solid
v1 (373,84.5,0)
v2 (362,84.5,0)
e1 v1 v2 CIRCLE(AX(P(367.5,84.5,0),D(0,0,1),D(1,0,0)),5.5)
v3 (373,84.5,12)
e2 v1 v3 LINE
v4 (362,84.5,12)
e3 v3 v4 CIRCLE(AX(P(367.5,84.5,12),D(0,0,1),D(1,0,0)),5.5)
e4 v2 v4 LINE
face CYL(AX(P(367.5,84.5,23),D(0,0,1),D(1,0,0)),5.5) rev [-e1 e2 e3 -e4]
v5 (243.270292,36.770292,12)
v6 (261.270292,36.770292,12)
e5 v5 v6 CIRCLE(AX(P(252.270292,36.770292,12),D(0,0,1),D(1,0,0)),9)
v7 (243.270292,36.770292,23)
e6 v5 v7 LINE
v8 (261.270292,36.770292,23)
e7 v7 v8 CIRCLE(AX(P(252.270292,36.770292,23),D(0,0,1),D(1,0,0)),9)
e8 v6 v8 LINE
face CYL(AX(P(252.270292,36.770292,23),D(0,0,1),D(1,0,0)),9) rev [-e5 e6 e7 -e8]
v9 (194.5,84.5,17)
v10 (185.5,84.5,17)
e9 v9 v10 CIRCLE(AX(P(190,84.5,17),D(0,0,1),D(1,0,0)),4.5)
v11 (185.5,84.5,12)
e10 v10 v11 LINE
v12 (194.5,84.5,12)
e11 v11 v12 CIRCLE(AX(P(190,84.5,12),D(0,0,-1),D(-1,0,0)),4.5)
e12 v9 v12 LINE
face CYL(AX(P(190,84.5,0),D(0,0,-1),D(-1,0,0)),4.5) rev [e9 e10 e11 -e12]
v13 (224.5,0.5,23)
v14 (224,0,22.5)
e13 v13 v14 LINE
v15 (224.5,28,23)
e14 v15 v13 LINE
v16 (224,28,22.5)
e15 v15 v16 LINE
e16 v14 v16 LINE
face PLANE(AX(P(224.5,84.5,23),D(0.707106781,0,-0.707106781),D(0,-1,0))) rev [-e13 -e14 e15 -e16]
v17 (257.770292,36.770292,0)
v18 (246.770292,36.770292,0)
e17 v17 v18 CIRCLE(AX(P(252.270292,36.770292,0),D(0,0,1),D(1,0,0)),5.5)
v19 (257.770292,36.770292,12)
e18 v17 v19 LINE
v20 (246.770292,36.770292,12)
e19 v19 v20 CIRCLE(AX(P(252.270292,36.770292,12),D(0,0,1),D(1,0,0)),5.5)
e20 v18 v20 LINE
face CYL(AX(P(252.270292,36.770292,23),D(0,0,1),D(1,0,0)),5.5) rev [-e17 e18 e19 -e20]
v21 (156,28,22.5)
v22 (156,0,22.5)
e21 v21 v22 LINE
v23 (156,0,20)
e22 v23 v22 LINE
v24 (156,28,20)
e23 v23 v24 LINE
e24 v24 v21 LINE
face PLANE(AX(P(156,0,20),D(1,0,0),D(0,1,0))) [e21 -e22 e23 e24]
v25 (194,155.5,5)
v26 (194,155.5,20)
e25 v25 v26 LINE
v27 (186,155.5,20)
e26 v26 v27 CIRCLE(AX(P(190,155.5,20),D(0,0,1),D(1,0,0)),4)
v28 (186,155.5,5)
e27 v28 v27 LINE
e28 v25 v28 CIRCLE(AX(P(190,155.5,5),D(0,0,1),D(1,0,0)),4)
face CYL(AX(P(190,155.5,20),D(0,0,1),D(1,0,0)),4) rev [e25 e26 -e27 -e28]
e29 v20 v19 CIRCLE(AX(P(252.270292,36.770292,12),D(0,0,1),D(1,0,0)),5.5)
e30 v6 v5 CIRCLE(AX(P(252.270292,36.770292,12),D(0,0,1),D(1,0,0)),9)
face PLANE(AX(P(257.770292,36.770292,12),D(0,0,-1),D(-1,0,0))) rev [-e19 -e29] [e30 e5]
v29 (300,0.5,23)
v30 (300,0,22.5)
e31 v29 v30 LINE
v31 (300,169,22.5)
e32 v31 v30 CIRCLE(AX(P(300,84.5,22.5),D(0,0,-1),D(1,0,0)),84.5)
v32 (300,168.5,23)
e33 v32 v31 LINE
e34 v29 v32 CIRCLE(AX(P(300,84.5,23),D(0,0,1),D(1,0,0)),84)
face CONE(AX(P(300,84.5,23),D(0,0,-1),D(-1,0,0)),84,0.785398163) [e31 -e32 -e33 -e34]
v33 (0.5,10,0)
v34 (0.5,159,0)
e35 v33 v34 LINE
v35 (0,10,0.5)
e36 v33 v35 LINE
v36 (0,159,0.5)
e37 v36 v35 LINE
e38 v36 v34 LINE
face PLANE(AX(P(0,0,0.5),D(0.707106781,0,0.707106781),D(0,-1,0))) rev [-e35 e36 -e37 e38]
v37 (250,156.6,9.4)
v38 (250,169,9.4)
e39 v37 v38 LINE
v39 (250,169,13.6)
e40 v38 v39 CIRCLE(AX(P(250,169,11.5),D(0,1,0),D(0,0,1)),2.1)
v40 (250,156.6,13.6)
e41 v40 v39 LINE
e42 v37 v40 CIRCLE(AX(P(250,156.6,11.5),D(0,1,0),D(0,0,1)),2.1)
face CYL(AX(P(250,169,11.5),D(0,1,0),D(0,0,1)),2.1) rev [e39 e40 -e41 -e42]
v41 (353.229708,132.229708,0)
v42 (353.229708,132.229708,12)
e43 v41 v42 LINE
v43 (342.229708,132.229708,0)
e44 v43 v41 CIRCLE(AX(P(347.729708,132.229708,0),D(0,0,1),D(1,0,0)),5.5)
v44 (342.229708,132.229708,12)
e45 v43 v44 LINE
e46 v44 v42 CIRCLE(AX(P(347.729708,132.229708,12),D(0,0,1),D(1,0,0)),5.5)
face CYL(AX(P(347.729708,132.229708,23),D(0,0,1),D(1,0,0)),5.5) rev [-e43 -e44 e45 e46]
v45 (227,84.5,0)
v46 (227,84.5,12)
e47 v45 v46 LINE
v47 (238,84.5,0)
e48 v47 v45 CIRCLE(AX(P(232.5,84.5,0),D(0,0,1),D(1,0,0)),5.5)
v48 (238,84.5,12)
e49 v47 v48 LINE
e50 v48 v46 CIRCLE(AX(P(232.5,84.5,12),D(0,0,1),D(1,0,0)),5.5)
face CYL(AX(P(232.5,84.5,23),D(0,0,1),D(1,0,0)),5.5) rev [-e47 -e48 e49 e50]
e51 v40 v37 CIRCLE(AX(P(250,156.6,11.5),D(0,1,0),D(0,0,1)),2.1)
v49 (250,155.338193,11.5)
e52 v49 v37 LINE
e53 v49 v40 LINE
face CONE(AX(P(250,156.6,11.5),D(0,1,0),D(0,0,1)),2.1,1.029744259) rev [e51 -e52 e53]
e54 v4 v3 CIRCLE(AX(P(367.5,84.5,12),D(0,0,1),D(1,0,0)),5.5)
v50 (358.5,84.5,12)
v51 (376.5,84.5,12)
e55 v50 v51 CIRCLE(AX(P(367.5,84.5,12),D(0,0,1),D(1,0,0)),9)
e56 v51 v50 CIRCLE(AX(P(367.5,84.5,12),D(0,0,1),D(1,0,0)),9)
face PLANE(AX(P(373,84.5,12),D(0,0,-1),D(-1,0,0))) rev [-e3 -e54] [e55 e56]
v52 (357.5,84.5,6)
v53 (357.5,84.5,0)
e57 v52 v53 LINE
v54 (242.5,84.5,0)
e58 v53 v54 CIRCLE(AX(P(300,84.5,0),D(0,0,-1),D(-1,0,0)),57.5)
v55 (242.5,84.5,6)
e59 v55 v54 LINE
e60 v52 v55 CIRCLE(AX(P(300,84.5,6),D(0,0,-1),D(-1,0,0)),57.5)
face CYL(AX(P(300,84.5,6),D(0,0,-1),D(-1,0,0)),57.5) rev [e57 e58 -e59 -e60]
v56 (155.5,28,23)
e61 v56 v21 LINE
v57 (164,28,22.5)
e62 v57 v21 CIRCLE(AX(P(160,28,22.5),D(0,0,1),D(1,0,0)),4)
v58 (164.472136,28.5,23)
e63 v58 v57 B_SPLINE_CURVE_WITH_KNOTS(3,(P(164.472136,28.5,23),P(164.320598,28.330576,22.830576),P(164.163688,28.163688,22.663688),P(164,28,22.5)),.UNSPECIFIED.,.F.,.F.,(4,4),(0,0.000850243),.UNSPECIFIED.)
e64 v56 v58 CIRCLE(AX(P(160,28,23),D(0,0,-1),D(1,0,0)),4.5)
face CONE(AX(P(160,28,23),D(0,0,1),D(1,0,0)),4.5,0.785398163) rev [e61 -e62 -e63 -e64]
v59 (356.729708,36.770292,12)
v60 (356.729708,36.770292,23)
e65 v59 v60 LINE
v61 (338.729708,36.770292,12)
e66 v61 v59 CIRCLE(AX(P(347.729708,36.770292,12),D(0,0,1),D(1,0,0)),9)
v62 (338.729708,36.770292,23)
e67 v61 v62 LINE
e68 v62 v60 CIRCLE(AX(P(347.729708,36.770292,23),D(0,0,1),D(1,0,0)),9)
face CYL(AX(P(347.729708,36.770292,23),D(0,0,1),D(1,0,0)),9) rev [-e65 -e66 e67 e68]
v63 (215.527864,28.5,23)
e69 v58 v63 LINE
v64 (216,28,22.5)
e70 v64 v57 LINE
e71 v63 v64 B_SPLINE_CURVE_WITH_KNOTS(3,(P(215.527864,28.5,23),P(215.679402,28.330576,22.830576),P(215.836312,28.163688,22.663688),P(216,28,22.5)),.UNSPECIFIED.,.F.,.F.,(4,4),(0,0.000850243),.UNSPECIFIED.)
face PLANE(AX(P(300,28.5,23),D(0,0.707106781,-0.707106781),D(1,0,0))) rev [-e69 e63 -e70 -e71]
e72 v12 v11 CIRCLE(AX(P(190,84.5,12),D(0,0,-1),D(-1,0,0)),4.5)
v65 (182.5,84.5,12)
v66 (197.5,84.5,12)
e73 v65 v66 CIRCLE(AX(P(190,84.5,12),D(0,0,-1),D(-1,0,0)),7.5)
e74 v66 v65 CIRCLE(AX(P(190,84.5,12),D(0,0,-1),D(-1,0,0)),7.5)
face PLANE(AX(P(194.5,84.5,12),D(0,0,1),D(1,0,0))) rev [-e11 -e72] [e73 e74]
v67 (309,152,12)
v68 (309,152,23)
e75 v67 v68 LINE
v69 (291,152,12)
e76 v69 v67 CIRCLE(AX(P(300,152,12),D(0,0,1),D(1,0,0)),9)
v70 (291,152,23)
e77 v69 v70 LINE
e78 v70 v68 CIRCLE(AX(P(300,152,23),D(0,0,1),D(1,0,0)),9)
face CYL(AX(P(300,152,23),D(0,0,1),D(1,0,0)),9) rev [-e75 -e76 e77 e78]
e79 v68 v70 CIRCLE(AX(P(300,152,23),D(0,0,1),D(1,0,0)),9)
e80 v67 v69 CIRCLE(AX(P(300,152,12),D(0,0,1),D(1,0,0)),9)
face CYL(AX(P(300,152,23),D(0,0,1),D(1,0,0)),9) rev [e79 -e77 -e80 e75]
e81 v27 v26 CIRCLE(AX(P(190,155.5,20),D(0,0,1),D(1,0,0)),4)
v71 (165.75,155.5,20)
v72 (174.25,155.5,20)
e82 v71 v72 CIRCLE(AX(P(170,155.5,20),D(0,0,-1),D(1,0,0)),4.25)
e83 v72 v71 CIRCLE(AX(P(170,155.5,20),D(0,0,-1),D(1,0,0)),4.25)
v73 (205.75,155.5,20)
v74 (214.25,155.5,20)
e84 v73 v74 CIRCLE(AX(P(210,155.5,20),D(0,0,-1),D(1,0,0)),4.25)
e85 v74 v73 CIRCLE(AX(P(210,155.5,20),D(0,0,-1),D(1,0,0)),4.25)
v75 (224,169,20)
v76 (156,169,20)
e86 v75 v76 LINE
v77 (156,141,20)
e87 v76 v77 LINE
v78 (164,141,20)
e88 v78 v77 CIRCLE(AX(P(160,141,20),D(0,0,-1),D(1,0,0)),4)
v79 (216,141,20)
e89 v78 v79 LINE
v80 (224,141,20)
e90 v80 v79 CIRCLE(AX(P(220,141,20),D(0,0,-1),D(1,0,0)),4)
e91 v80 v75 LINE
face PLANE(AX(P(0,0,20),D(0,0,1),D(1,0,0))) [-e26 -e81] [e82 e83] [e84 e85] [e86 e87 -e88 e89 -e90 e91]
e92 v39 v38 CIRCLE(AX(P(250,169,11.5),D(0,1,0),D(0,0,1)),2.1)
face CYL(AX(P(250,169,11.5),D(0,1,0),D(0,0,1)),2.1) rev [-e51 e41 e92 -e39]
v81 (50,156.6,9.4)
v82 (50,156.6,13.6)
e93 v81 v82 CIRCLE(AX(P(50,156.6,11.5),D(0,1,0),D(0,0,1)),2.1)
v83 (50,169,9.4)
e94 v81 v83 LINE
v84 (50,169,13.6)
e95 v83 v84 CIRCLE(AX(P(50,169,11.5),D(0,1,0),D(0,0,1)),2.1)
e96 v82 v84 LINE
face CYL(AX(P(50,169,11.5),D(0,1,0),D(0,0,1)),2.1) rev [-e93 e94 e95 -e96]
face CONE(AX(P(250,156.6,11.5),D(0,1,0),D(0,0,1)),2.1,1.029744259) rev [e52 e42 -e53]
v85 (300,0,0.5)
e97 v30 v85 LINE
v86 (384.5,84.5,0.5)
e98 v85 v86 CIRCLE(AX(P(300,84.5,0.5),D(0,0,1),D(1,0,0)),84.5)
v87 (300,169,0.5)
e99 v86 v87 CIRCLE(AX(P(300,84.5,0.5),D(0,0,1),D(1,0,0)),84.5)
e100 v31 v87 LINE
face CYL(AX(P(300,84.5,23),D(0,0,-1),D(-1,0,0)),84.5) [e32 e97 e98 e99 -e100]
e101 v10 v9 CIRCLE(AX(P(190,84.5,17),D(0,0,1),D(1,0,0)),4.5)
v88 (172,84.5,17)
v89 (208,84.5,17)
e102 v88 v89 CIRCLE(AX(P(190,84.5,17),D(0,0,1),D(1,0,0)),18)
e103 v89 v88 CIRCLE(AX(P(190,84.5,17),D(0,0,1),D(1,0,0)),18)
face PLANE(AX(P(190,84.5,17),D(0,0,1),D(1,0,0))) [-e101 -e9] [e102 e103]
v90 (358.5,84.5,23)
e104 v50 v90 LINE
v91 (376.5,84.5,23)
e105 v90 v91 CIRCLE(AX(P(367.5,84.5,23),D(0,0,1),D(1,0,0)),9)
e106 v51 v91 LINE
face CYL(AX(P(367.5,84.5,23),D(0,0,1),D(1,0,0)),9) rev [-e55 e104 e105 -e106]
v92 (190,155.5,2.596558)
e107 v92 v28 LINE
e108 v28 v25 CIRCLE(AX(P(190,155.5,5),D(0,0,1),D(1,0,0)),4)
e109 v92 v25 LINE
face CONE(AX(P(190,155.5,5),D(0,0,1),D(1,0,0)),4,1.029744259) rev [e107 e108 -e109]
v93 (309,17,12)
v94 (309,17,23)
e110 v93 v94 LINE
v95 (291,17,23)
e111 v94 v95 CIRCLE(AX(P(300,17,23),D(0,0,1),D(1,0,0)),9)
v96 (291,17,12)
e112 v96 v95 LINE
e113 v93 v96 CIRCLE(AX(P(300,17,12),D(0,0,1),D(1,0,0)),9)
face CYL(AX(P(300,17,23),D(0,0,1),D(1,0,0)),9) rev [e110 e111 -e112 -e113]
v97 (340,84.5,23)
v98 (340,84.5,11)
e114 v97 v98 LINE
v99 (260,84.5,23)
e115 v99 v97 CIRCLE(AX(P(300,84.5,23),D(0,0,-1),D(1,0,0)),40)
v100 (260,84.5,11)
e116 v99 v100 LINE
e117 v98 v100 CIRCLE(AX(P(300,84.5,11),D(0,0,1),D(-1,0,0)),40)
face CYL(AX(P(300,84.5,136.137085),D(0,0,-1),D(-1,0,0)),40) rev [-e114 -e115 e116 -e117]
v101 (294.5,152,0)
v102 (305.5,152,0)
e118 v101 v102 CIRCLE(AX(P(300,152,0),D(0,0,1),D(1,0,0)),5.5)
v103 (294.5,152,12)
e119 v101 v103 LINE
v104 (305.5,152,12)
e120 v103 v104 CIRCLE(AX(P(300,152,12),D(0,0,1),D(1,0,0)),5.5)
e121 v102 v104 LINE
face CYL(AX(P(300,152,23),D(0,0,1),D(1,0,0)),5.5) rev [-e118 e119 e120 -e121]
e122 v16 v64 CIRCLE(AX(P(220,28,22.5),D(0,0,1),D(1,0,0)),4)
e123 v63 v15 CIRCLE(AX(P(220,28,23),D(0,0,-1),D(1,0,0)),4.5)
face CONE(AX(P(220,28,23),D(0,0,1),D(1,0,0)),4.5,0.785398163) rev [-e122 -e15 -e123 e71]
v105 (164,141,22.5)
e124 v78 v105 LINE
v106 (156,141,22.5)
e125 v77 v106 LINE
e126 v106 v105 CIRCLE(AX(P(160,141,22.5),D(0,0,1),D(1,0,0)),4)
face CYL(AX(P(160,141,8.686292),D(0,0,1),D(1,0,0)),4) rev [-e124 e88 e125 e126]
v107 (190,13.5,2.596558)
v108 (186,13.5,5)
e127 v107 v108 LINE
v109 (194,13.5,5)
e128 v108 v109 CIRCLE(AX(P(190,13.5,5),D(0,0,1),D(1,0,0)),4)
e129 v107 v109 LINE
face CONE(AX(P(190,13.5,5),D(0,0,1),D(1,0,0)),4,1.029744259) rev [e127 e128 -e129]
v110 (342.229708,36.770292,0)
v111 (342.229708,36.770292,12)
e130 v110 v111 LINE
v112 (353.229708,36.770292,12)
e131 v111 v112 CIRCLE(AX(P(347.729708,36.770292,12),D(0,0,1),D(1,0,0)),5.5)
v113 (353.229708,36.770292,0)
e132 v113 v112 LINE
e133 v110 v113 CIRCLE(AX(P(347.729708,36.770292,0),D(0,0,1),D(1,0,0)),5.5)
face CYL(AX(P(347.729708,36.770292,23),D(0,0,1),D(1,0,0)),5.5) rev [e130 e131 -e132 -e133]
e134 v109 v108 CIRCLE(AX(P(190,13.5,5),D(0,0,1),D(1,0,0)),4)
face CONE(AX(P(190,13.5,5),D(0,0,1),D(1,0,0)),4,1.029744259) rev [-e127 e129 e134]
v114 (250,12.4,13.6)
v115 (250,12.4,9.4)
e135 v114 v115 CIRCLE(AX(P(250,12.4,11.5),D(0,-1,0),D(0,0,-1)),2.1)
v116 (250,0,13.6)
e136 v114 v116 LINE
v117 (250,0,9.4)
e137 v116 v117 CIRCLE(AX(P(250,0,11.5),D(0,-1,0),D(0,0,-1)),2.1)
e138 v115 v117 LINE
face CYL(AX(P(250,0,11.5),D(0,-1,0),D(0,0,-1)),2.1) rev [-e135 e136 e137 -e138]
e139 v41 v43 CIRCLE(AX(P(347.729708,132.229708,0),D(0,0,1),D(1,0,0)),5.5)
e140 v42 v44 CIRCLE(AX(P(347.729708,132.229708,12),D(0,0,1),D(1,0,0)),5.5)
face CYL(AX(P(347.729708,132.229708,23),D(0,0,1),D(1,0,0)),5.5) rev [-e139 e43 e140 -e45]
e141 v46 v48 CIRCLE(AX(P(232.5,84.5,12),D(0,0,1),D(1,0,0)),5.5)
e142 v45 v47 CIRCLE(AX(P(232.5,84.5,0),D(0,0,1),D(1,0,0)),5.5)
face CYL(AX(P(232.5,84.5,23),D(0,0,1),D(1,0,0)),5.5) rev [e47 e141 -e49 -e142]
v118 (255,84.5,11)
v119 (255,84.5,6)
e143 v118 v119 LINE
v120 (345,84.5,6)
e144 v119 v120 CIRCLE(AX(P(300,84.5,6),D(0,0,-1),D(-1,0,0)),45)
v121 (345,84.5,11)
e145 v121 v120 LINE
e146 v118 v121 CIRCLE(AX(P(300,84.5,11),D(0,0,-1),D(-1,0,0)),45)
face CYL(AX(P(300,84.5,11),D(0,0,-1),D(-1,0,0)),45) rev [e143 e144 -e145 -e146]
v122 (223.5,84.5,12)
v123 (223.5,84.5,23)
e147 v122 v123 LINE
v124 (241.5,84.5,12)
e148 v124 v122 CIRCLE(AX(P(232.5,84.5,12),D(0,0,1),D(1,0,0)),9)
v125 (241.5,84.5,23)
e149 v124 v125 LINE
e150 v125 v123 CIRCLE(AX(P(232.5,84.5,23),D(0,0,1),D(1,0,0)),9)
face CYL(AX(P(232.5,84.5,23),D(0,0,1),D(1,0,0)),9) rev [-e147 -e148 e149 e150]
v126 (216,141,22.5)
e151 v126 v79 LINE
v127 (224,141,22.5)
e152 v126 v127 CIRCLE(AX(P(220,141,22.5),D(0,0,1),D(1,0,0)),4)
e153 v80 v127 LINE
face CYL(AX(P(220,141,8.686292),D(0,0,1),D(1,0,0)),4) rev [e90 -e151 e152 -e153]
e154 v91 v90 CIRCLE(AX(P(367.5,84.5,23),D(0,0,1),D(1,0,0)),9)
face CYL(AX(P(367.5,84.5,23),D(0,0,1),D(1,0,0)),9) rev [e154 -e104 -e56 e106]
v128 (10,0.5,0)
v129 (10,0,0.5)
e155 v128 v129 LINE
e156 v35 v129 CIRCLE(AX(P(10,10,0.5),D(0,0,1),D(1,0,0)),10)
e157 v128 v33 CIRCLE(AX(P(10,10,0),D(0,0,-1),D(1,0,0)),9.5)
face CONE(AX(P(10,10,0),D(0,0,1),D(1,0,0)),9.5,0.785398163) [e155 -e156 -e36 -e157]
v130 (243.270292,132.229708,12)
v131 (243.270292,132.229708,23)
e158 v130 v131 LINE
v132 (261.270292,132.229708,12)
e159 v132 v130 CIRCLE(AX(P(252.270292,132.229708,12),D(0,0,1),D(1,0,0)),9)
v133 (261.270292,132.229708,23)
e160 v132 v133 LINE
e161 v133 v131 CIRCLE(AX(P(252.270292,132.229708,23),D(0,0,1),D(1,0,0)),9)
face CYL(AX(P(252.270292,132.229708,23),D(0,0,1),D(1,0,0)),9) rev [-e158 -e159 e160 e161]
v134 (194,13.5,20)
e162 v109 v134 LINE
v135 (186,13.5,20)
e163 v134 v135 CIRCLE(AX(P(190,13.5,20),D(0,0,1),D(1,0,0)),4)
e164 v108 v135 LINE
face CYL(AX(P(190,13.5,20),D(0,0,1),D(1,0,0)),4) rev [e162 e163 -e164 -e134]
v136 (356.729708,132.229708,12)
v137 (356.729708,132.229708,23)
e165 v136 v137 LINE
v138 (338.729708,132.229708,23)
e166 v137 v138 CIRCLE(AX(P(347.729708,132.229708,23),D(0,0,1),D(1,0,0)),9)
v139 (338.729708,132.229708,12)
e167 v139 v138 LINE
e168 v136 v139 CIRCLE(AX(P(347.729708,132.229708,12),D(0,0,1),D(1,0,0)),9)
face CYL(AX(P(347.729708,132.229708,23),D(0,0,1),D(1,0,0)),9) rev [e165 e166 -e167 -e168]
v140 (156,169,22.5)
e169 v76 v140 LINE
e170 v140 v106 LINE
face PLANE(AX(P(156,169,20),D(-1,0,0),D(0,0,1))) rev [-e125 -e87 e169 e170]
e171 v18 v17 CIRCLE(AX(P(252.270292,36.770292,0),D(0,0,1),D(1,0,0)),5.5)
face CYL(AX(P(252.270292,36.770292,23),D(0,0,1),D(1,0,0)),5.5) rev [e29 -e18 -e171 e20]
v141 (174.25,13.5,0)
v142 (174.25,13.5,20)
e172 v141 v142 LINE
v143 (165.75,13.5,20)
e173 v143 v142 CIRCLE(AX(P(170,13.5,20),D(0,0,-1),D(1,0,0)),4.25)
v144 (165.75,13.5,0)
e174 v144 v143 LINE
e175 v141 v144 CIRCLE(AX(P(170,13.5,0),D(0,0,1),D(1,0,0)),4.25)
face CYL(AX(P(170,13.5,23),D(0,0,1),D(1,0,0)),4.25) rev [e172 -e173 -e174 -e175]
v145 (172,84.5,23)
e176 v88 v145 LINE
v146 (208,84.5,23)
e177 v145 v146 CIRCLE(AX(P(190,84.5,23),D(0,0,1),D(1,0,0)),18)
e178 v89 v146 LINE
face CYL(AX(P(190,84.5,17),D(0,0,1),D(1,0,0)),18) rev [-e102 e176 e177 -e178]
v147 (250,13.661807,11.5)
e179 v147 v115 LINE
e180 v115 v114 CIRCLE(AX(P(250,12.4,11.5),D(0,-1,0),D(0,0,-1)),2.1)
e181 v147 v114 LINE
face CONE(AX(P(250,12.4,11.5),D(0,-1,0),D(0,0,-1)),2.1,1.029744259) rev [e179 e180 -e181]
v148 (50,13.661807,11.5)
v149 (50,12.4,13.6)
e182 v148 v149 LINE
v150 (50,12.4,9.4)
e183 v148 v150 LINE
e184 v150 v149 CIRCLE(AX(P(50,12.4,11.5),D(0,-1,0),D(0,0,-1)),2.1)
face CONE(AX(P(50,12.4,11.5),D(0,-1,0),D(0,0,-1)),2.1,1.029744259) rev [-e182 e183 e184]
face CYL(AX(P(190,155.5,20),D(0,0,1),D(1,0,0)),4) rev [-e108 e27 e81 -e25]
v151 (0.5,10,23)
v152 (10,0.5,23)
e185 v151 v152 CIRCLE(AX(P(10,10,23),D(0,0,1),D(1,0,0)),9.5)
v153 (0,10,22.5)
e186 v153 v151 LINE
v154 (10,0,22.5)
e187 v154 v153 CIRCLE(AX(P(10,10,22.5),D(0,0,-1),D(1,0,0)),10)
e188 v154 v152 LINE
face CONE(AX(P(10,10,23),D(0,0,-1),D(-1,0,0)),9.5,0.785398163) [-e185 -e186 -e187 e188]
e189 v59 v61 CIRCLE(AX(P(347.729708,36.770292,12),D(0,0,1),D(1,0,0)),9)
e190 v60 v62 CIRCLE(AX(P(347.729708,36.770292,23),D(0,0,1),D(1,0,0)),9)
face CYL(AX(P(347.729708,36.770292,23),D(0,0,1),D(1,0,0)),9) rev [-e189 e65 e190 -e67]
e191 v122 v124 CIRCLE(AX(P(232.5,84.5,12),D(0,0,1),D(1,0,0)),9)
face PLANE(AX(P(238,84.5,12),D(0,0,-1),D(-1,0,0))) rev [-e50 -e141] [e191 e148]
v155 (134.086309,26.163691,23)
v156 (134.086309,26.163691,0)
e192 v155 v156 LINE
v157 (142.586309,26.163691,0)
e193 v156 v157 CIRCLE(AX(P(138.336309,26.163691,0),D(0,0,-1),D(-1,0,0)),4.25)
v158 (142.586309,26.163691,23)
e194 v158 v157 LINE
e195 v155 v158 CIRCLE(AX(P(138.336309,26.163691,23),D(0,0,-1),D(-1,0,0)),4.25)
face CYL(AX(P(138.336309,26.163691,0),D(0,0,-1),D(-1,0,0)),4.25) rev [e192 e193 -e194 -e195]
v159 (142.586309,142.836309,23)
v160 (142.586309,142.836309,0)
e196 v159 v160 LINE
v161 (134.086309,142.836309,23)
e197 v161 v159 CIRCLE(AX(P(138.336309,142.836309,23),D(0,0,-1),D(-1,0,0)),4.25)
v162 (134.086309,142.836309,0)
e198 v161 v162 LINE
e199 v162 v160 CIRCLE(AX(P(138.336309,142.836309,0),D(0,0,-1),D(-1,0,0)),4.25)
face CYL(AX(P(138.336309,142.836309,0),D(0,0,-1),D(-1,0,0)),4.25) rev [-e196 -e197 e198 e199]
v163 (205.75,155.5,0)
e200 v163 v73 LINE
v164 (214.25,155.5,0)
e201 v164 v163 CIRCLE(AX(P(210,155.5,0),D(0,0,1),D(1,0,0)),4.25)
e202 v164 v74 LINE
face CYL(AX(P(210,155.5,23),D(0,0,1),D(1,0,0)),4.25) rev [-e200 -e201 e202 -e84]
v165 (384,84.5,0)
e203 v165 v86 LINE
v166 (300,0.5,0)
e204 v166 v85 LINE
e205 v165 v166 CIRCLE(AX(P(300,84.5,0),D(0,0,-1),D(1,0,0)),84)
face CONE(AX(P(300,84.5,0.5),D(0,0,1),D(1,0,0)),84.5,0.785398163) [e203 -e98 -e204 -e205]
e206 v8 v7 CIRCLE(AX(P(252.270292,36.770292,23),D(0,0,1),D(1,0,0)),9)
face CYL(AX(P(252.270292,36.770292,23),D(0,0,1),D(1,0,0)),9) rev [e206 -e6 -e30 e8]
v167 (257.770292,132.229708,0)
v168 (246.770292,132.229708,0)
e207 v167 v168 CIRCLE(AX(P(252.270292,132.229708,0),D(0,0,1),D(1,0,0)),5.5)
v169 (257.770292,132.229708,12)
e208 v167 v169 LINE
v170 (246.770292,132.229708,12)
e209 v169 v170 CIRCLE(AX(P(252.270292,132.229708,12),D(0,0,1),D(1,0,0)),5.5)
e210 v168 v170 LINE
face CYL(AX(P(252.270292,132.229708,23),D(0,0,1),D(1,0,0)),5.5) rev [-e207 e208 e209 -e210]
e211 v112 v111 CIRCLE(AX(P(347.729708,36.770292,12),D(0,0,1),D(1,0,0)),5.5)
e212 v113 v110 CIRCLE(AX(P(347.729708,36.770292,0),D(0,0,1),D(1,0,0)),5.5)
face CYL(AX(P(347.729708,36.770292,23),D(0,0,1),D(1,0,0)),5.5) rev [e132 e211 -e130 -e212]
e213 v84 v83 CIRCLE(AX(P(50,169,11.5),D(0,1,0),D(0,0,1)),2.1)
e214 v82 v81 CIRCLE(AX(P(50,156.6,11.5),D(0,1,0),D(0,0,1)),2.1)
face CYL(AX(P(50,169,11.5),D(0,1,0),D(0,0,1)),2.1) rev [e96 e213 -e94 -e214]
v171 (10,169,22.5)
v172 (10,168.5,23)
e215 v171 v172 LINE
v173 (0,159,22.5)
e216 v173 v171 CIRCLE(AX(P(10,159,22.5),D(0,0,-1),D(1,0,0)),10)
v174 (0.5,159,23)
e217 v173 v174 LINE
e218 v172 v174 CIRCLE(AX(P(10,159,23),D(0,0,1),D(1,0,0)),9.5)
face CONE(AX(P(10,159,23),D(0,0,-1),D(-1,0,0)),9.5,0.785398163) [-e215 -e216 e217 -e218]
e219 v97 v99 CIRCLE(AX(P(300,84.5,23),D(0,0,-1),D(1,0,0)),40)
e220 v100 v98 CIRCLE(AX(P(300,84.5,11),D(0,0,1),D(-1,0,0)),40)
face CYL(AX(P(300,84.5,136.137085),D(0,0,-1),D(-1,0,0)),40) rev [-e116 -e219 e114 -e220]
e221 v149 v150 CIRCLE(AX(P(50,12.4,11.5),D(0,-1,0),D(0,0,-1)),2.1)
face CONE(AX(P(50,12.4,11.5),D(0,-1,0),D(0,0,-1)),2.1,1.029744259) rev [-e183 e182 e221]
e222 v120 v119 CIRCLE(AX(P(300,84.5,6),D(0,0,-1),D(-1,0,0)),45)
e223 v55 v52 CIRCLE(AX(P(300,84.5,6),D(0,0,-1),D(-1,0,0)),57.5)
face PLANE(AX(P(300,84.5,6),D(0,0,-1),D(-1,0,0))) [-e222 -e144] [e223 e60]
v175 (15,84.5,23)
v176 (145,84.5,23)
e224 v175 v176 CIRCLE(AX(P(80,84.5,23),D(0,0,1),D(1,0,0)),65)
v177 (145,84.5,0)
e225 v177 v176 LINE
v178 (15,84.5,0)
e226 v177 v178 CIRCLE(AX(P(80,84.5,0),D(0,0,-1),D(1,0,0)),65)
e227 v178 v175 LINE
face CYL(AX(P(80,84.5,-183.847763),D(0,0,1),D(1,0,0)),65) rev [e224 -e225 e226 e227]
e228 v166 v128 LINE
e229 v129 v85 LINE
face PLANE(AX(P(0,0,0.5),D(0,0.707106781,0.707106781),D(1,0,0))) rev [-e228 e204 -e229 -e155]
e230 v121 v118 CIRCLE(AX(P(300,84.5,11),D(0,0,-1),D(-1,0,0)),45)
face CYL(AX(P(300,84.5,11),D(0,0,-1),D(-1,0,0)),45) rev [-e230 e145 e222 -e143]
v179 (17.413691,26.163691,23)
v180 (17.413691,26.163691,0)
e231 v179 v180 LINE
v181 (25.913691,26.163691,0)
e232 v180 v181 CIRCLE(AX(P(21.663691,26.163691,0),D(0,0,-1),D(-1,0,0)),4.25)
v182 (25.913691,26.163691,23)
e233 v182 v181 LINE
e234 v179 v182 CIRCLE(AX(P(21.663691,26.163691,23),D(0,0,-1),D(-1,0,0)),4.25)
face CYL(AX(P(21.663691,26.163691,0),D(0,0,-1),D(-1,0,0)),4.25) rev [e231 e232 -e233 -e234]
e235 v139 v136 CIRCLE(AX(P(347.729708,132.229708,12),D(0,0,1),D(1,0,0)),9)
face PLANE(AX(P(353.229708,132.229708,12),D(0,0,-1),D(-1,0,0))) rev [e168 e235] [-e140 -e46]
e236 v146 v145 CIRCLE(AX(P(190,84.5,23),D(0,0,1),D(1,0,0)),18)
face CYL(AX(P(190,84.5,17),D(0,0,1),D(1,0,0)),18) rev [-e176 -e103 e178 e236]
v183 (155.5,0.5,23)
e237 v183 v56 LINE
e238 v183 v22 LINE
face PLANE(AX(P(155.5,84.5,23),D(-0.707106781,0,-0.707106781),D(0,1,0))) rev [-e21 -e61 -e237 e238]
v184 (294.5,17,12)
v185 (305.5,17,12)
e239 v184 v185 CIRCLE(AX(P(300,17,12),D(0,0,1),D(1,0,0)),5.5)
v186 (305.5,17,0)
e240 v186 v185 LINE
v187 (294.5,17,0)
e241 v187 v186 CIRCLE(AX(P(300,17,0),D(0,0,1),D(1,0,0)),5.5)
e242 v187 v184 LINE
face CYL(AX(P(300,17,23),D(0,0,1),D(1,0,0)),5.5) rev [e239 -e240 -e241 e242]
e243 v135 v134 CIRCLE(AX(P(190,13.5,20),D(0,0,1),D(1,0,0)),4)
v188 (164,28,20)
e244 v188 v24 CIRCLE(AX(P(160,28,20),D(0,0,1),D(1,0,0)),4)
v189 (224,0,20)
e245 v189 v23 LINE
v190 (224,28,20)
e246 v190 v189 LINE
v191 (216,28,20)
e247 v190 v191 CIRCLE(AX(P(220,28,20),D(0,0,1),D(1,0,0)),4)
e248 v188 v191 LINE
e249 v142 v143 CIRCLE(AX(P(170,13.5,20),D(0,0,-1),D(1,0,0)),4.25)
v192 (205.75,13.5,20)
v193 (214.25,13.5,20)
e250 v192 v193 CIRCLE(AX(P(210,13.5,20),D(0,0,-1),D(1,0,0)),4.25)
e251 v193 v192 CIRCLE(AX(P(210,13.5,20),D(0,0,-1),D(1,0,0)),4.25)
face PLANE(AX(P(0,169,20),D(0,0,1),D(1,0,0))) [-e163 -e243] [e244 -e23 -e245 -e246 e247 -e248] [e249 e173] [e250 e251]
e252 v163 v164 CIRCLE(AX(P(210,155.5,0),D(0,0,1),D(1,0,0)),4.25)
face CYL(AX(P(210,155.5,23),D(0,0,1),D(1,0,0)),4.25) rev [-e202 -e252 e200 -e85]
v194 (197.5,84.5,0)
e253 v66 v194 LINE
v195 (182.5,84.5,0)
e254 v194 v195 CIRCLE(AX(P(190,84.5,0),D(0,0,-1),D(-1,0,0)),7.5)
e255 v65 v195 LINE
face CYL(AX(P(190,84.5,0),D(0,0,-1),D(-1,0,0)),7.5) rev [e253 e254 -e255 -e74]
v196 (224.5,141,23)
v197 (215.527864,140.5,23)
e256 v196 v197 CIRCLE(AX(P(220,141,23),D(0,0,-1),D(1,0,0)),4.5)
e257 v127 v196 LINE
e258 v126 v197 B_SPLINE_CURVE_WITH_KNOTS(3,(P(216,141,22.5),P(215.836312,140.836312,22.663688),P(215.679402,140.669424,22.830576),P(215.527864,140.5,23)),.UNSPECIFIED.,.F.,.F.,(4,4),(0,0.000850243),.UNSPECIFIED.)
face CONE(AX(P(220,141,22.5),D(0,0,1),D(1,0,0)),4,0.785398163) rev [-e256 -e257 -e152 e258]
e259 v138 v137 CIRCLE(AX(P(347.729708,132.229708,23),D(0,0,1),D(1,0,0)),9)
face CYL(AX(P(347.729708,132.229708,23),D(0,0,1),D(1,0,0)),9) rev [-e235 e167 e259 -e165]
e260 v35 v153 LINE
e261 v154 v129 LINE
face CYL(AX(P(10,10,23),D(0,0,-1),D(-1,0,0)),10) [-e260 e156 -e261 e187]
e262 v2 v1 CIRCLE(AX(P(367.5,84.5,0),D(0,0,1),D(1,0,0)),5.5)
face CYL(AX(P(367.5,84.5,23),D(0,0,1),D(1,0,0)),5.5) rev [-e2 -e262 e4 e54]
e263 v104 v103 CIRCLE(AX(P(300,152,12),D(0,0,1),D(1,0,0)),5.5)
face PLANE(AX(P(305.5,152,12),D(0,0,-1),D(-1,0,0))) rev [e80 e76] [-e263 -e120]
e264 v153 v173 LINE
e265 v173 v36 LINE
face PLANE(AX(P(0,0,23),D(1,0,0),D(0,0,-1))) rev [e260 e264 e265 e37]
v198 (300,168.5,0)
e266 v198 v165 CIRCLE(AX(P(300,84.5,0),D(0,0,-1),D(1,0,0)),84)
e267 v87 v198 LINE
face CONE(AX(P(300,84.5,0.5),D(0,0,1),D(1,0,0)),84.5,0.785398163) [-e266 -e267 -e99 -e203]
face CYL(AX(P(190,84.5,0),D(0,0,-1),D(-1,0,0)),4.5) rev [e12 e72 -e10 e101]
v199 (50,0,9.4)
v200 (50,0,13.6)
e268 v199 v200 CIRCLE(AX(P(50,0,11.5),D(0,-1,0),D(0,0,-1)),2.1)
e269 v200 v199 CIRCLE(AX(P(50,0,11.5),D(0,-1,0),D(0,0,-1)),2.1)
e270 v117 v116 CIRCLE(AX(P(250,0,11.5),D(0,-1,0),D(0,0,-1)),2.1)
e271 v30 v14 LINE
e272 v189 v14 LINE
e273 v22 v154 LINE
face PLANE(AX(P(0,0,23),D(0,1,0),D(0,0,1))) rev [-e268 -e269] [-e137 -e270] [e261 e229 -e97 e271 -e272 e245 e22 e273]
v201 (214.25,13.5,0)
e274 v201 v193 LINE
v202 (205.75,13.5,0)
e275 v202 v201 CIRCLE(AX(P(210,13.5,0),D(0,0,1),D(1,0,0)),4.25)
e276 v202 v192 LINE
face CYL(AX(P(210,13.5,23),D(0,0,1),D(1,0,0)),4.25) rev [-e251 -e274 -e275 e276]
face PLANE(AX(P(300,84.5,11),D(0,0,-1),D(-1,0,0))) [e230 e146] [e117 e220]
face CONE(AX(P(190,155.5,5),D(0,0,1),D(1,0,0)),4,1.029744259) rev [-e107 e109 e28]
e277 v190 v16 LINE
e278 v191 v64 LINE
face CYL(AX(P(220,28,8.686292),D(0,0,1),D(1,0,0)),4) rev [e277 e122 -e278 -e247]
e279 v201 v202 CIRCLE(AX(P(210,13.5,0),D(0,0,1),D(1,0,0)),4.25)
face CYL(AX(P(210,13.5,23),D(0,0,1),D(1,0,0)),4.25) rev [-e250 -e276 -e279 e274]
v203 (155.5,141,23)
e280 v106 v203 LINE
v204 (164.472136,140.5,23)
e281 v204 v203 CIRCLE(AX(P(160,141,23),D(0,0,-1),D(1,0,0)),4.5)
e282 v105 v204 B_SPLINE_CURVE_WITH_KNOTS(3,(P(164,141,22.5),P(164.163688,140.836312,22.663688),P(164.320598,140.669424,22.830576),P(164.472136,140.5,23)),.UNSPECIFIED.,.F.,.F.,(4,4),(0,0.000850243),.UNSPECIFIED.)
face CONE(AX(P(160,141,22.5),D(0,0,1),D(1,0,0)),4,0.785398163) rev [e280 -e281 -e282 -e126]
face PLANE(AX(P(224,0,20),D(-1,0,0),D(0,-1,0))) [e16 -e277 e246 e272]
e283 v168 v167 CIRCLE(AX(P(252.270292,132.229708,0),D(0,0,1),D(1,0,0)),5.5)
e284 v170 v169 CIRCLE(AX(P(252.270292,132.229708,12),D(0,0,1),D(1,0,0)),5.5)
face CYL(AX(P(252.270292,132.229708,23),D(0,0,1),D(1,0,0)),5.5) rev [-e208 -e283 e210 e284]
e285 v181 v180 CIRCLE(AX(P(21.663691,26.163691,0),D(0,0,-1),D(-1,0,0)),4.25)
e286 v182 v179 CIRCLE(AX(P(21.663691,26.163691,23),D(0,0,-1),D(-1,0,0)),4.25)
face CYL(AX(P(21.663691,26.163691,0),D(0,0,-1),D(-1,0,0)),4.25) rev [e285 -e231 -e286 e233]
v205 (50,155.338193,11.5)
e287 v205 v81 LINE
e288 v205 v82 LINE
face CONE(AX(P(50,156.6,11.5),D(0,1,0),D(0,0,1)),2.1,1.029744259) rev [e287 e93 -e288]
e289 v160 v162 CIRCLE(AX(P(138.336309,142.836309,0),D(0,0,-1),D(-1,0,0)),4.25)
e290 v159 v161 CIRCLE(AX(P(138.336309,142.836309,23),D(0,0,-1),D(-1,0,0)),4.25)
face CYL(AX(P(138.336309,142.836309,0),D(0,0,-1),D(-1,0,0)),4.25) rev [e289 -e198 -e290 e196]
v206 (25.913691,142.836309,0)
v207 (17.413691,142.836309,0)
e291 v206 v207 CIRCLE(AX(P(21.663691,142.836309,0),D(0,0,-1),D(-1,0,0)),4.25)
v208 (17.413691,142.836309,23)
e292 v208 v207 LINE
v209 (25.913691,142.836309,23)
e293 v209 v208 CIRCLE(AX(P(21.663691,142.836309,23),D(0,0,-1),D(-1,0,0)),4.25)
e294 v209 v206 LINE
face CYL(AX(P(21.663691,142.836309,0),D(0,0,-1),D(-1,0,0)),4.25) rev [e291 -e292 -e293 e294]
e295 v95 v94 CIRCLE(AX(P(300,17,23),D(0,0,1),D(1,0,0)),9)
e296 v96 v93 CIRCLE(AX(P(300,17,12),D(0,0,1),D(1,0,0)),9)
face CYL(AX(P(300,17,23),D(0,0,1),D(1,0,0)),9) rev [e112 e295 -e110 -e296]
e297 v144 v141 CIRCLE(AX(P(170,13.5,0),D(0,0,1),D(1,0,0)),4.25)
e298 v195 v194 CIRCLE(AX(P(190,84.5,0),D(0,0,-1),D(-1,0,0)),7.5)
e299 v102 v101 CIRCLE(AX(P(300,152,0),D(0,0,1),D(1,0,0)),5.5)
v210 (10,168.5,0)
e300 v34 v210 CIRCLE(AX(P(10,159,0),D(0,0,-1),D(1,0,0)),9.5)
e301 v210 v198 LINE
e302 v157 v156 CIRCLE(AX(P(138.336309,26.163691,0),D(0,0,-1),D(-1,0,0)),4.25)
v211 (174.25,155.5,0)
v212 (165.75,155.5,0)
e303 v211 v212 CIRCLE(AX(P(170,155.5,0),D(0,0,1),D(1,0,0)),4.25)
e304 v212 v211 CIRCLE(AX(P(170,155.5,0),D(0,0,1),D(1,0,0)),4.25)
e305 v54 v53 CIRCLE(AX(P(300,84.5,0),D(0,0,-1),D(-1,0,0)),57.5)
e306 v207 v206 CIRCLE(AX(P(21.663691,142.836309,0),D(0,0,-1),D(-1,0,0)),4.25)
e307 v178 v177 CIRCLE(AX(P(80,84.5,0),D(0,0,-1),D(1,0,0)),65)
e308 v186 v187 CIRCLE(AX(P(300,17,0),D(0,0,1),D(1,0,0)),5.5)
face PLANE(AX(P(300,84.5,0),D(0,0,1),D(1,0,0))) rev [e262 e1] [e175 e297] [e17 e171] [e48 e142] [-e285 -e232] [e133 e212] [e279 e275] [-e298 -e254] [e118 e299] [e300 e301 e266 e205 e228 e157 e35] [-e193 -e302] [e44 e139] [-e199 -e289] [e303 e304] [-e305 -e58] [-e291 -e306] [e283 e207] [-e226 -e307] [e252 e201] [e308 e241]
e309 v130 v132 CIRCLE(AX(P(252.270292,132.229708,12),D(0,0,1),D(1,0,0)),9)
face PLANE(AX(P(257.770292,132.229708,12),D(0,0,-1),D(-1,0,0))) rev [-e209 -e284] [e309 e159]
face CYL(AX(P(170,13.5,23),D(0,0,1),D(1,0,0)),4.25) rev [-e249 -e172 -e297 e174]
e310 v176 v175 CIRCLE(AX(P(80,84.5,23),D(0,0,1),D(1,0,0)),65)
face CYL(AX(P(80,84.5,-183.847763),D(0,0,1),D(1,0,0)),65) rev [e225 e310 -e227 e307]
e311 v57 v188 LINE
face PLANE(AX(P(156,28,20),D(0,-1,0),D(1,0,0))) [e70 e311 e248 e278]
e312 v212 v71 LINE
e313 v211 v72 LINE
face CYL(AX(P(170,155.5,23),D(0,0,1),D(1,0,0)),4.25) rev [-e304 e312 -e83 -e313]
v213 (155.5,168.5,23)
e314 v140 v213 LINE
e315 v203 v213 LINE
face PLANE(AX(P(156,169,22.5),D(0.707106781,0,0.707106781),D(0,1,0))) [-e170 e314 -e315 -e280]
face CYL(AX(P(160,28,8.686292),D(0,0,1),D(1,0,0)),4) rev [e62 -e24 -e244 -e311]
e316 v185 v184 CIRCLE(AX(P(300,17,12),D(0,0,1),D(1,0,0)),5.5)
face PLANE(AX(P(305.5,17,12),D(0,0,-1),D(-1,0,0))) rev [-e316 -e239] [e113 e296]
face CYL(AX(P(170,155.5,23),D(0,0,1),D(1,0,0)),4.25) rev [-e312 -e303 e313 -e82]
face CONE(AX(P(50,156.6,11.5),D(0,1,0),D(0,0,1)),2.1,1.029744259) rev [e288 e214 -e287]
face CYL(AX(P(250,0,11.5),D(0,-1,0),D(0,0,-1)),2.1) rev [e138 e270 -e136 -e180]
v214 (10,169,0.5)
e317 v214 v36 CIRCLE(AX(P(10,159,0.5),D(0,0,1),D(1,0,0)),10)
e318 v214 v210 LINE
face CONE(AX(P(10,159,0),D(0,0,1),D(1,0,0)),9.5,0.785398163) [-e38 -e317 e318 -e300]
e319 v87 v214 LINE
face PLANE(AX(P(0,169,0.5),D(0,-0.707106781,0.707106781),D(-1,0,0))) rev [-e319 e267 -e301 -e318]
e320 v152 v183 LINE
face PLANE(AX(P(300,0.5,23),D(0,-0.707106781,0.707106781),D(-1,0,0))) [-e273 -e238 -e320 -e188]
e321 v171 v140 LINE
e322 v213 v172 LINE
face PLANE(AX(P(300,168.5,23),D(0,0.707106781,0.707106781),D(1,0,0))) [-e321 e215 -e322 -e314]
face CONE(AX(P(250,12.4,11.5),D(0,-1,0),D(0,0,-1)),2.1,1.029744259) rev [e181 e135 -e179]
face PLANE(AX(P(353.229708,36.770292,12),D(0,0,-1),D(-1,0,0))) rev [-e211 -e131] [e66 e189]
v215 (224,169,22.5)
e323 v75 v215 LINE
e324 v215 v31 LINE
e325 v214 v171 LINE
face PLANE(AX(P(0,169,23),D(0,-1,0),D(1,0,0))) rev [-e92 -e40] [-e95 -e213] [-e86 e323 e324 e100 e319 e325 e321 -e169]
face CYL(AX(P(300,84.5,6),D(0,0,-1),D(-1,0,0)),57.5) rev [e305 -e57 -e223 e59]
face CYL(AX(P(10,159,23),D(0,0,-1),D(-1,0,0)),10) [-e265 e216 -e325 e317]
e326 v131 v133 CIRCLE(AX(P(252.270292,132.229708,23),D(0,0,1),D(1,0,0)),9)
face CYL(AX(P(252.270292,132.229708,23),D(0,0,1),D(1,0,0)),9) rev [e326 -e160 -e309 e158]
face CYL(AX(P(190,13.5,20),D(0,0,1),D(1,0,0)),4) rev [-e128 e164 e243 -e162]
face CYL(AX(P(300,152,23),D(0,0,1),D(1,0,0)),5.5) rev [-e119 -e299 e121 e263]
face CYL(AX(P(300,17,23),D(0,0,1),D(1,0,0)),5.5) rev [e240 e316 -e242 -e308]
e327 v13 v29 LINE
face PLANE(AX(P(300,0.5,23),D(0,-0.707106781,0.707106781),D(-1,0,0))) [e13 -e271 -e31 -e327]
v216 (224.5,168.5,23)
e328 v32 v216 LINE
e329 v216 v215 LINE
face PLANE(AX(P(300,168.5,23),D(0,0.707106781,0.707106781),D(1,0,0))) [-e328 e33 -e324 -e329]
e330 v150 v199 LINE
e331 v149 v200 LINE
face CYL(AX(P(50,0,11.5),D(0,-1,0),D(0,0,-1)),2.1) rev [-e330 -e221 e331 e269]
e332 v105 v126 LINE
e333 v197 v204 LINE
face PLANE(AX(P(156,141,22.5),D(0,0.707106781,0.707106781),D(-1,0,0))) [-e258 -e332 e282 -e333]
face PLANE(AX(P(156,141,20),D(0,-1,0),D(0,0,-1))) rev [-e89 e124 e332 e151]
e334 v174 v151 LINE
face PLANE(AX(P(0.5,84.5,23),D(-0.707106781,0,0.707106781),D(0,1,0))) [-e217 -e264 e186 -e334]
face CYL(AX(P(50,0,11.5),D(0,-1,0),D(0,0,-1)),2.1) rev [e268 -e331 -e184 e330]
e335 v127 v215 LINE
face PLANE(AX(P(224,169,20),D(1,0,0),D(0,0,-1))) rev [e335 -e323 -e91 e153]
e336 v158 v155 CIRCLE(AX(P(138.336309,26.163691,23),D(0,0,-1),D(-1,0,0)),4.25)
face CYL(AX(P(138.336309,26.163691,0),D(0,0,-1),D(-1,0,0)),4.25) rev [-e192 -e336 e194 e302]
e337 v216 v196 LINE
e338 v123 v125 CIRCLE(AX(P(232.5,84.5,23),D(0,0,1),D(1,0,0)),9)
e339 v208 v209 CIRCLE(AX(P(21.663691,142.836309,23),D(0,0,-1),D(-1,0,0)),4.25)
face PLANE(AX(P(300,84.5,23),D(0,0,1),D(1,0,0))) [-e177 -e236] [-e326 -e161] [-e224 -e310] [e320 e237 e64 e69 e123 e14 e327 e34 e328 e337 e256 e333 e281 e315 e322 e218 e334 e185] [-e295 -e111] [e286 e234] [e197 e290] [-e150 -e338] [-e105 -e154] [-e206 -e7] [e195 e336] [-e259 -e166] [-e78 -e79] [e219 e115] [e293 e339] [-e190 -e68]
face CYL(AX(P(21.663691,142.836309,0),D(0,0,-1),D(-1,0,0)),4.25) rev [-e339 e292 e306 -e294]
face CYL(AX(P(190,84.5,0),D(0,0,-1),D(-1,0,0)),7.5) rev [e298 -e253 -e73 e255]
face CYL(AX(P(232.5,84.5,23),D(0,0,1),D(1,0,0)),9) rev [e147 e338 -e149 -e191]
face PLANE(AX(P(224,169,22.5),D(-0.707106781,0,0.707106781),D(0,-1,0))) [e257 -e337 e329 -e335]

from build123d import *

# Parameters (mm, degrees)
BOSS_EXTRUDE1_DEPTH                                = 23
FILLET1_R                                          = 10
HOLE_SIZE_BASED_ON_SOCKET_HEAD_CAP_SCR_D           = 11
HOLE_SIZE_BASED_ON_SOCKET_HEAD_CAP_SCR_CBORE_D     = 18
HOLE_SIZE_BASED_ON_SOCKET_HEAD_CAP_SCR_CBORE_DEPTH = 11
CIRPATTERN1_COUNT                                  = 8
SKETCH8_R                                          = 65
CUT_EXTRUDE1_DEPTH                                 = 23
SKETCH9_R                                          = 18
CUT_EXTRUDE2_DEPTH                                 = 6
HOLE_WIZARD_3_D                                    = 9
HOLE_WIZARD_3_CBORE_D                              = 15
HOLE_WIZARD_3_CBORE_DEPTH                          = 12
SKETCH13_R                                         = 40
CUT_EXTRUDE3_DEPTH                                 = 23
SKETCH14_R                                         = 57.5
CUT_EXTRUDE4_DEPTH                                 = 6
M10_TAPPED_HOLE3_D                                 = 8.5
M5_TAPPED_HOLE1_AT_2_COUNT                         = 2
M5_TAPPED_HOLE1_AT_2_PITCH                         = 200
M10_TAPPED_HOLE5_D                                 = 8.5
CHAMFER1_SIZE                                      = 0.5
SKETCH23_R                                         = 45
CUT_EXTRUDE5_DEPTH                                 = 5
SKETCH24_W                                         = 68
SKETCH24_H                                         = 28
CUT_EXTRUDE6_DEPTH                                 = 3
SKETCH25_R                                         = 4
CUT_EXTRUDE7_DEPTH                                 = 3
CHAMFER2_SIZE                                      = 0.5


with BuildPart() as part:
    # Sketch1 → Boss-Extrude1 (new body)
    with BuildSketch(Plane.XY):
        with BuildLine():
            Line((0, 0), (300, 0))
            ThreePointArc((300, 0), (384.5, 84.5), (300, 169))
            Line((300, 169), (0, 169))
            Line((0, 169), (0, 0))
        make_face()
    extrude(amount=BOSS_EXTRUDE1_DEPTH)

    # Fillet1
    fillet1_edges = [part.edges().sort_by_distance(p)[0] for p in [
        (0, 169, 11.5),
        (0, 0, 11.5),
    ]]
    fillet(fillet1_edges, radius=FILLET1_R)

    # Hole size (% based on socket head cap screw type)3 (through all)
    with Locations(Plane.XY.offset(23)):
        with Locations((300, 17)):
            hole_size_based_on_socket_head_cap_scr = CounterBoreHole(HOLE_SIZE_BASED_ON_SOCKET_HEAD_CAP_SCR_D / 2, HOLE_SIZE_BASED_ON_SOCKET_HEAD_CAP_SCR_CBORE_D / 2, HOLE_SIZE_BASED_ON_SOCKET_HEAD_CAP_SCR_CBORE_DEPTH)

    # CirPattern1: Hole size (% based on socket head cap screw type)3 ×8 about axis
    cirpattern1_axis = Axis((300, 84.5, 0), (0, 0, 1))
    for i in range(1, CIRPATTERN1_COUNT):
        add(hole_size_based_on_socket_head_cap_scr.rotate(cirpattern1_axis, i * 360 / CIRPATTERN1_COUNT), mode=Mode.SUBTRACT)

    # Sketch8 → Cut-Extrude1 (cut)
    with BuildSketch(Plane.XY.offset(23)):
        with Locations((80, 84.5)):
            Circle(SKETCH8_R)
    extrude(amount=-CUT_EXTRUDE1_DEPTH, mode=Mode.SUBTRACT)

    # Sketch9 → Cut-Extrude2 (cut)
    with BuildSketch(Plane.XY.offset(23)):
        with Locations((190, 84.5)):
            Circle(SKETCH9_R)
    extrude(amount=-CUT_EXTRUDE2_DEPTH, mode=Mode.SUBTRACT)

    # Hole Wizard 3 (through all)
    with Locations(Plane(origin=(0, 0, 0), x_dir=(-1, 0, 0), z_dir=(0, 0, -1))):
        with Locations((-190, 84.5)):
            CounterBoreHole(HOLE_WIZARD_3_D / 2, HOLE_WIZARD_3_CBORE_D / 2, HOLE_WIZARD_3_CBORE_DEPTH)

    # Sketch13 → Cut-Extrude3 (cut)
    with BuildSketch(Plane(origin=(0, 0, 0), x_dir=(-1, 0, 0), z_dir=(0, 0, -1))):
        with Locations((-300, 84.5)):
            Circle(SKETCH13_R)
    extrude(amount=-CUT_EXTRUDE3_DEPTH, mode=Mode.SUBTRACT)

    # Sketch14 → Cut-Extrude4 (cut)
    with BuildSketch(Plane(origin=(0, 0, 0), x_dir=(-1, 0, 0), z_dir=(0, 0, -1))):
        with Locations((-300, 84.5)):
            Circle(SKETCH14_R)
    extrude(amount=-CUT_EXTRUDE4_DEPTH, mode=Mode.SUBTRACT)

    # M10 Tapped Hole3 (through all)
    with Locations(Plane(origin=(0, 0, 0), x_dir=(-1, 0, 0), z_dir=(0, 0, -1))):
        with Locations((-21.663690552, 26.163690552), (-138.336309448, 26.163690552), (-21.663690552, 142.836309448), (-138.336309448, 142.836309448), (-80, 84.5)):
            Hole(M10_TAPPED_HOLE3_D / 2)

    # Sketch18 → M5 Tapped Hole1 (revolve, cut)
    with BuildSketch(Plane(origin=(50, 169, 11.5), x_dir=(0, 0, 1), z_dir=(1, 0, 0))):
        Polygon((0, 0), (0, 13.6618073), (2.1, 12.4), (2.1, 0), align=None)
    m5_tapped_hole1 = revolve(axis=Axis((50, 175.35, 11.5), (0, -1, 0)), mode=Mode.SUBTRACT)

    # M5 Tapped Hole1 at 2: M5 Tapped Hole1 ×2
    with Locations(*[(i * M5_TAPPED_HOLE1_AT_2_PITCH, 0, 0) for i in range(1, M5_TAPPED_HOLE1_AT_2_COUNT)]):
        add(m5_tapped_hole1, mode=Mode.SUBTRACT)

    # Mirror1: M5 Tapped Hole1 across plane
    add(m5_tapped_hole1.mirror(Plane.ZX.offset(84.5)), mode=Mode.SUBTRACT)

    # Mirror1 copy 1 sketch → Mirror1 copy 1 (revolve, cut)
    with BuildSketch(Plane(origin=(250, 0, 11.5), x_dir=(0, 0, 1), z_dir=(1, 0, 0))):
        Polygon((0, 0), (0, -13.6618073), (2.1, -12.4), (2.1, 0), align=None)
    revolve(axis=Axis((250, -6.35, 11.5), (0, -1, 0)), mode=Mode.SUBTRACT)

    # M10 Tapped Hole5 (through all)
    with Locations(Plane.XY.offset(23)):
        with Locations((170, 155.5), (210, 155.5)):
            m10_tapped_hole5 = Hole(M10_TAPPED_HOLE5_D / 2)

    # Mirror2: M10 Tapped Hole5 across plane
    add(m10_tapped_hole5.mirror(Plane.ZX.offset(84.5)), mode=Mode.SUBTRACT)

    # Chamfer1
    chamfer1_edges = [part.edges().sort_by_distance(p)[0] for p in [
        (155, 0, 0),
        (0, 84.5, 0),
        (2.928932188, 166.071067812, 0),
        (2.928932188, 2.928932188, 0),
        (155, 169, 0),
        (384.5, 84.5, 0),
    ]]
    chamfer(chamfer1_edges, length=CHAMFER1_SIZE)

    # Sketch23 → Cut-Extrude5 (cut)
    with BuildSketch(Plane(origin=(0, 0, 6), x_dir=(-1, 0, 0), z_dir=(0, 0, -1))):
        with Locations((-300, 84.5)):
            Circle(SKETCH23_R)
    extrude(amount=-CUT_EXTRUDE5_DEPTH, mode=Mode.SUBTRACT)

    # Sketch24 → Cut-Extrude6 (cut)
    with BuildSketch(Plane.XY.offset(23)):
        with Locations((190, 155)):
            Rectangle(SKETCH24_W, SKETCH24_H)
    cut_extrude6 = extrude(amount=-CUT_EXTRUDE6_DEPTH, mode=Mode.SUBTRACT)

    # Mirror3: Cut-Extrude6 across plane
    add(cut_extrude6.mirror(Plane.ZX.offset(84.5)), mode=Mode.SUBTRACT)

    # Sketch25 → Cut-Extrude7 (cut)
    with BuildSketch(Plane.XY.offset(23)):
        with Locations((160, 141)):
            Circle(SKETCH25_R)
        with Locations((220, 141)):
            Circle(SKETCH25_R)
    cut_extrude7 = extrude(amount=-CUT_EXTRUDE7_DEPTH, mode=Mode.SUBTRACT)

    # Mirror4: Cut-Extrude7 across plane
    add(cut_extrude7.mirror(Plane.ZX.offset(84.5)), mode=Mode.SUBTRACT)

    # Sketch28 → Size mm, blind dowel hole 1 (revolve, cut)
    with BuildSketch(Plane(origin=(190, 13.5, 20), x_dir=(0, -1, 0), z_dir=(1, 0, 0))):
        Polygon((0, 0), (0, 17.403442476), (4, 15), (4, 0), align=None)
    size_mm_blind_dowel_hole_1 = revolve(axis=Axis((190, 13.5, 26.35), (0, 0, -1)), mode=Mode.SUBTRACT)

    # Mirror5: Size mm, blind dowel hole 1 across plane
    add(size_mm_blind_dowel_hole_1.mirror(Plane.ZX.offset(84.5)), mode=Mode.SUBTRACT)

    # Chamfer2
    chamfer2_edges = [part.edges().sort_by_distance(p)[0] for p in [
        (384.5, 84.5, 23),
        (262, 169, 23),
        (83, 0, 23),
        (0, 84.5, 23),
        (2.928932188, 166.071067812, 23),
        (2.928932188, 2.928932188, 23),
        (83, 169, 23),
        (156, 155, 23),
        (224, 155, 23),
        (262, 0, 23),
        (156, 14, 23),
        (224, 14, 23),
        (190, 141, 23),
        (160, 137, 23),
        (220, 137, 23),
        (190, 28, 23),
        (160, 32, 23),
        (220, 32, 23),
    ]]
    chamfer(chamfer2_edges, length=CHAMFER2_SIZE)


solid = part.part
